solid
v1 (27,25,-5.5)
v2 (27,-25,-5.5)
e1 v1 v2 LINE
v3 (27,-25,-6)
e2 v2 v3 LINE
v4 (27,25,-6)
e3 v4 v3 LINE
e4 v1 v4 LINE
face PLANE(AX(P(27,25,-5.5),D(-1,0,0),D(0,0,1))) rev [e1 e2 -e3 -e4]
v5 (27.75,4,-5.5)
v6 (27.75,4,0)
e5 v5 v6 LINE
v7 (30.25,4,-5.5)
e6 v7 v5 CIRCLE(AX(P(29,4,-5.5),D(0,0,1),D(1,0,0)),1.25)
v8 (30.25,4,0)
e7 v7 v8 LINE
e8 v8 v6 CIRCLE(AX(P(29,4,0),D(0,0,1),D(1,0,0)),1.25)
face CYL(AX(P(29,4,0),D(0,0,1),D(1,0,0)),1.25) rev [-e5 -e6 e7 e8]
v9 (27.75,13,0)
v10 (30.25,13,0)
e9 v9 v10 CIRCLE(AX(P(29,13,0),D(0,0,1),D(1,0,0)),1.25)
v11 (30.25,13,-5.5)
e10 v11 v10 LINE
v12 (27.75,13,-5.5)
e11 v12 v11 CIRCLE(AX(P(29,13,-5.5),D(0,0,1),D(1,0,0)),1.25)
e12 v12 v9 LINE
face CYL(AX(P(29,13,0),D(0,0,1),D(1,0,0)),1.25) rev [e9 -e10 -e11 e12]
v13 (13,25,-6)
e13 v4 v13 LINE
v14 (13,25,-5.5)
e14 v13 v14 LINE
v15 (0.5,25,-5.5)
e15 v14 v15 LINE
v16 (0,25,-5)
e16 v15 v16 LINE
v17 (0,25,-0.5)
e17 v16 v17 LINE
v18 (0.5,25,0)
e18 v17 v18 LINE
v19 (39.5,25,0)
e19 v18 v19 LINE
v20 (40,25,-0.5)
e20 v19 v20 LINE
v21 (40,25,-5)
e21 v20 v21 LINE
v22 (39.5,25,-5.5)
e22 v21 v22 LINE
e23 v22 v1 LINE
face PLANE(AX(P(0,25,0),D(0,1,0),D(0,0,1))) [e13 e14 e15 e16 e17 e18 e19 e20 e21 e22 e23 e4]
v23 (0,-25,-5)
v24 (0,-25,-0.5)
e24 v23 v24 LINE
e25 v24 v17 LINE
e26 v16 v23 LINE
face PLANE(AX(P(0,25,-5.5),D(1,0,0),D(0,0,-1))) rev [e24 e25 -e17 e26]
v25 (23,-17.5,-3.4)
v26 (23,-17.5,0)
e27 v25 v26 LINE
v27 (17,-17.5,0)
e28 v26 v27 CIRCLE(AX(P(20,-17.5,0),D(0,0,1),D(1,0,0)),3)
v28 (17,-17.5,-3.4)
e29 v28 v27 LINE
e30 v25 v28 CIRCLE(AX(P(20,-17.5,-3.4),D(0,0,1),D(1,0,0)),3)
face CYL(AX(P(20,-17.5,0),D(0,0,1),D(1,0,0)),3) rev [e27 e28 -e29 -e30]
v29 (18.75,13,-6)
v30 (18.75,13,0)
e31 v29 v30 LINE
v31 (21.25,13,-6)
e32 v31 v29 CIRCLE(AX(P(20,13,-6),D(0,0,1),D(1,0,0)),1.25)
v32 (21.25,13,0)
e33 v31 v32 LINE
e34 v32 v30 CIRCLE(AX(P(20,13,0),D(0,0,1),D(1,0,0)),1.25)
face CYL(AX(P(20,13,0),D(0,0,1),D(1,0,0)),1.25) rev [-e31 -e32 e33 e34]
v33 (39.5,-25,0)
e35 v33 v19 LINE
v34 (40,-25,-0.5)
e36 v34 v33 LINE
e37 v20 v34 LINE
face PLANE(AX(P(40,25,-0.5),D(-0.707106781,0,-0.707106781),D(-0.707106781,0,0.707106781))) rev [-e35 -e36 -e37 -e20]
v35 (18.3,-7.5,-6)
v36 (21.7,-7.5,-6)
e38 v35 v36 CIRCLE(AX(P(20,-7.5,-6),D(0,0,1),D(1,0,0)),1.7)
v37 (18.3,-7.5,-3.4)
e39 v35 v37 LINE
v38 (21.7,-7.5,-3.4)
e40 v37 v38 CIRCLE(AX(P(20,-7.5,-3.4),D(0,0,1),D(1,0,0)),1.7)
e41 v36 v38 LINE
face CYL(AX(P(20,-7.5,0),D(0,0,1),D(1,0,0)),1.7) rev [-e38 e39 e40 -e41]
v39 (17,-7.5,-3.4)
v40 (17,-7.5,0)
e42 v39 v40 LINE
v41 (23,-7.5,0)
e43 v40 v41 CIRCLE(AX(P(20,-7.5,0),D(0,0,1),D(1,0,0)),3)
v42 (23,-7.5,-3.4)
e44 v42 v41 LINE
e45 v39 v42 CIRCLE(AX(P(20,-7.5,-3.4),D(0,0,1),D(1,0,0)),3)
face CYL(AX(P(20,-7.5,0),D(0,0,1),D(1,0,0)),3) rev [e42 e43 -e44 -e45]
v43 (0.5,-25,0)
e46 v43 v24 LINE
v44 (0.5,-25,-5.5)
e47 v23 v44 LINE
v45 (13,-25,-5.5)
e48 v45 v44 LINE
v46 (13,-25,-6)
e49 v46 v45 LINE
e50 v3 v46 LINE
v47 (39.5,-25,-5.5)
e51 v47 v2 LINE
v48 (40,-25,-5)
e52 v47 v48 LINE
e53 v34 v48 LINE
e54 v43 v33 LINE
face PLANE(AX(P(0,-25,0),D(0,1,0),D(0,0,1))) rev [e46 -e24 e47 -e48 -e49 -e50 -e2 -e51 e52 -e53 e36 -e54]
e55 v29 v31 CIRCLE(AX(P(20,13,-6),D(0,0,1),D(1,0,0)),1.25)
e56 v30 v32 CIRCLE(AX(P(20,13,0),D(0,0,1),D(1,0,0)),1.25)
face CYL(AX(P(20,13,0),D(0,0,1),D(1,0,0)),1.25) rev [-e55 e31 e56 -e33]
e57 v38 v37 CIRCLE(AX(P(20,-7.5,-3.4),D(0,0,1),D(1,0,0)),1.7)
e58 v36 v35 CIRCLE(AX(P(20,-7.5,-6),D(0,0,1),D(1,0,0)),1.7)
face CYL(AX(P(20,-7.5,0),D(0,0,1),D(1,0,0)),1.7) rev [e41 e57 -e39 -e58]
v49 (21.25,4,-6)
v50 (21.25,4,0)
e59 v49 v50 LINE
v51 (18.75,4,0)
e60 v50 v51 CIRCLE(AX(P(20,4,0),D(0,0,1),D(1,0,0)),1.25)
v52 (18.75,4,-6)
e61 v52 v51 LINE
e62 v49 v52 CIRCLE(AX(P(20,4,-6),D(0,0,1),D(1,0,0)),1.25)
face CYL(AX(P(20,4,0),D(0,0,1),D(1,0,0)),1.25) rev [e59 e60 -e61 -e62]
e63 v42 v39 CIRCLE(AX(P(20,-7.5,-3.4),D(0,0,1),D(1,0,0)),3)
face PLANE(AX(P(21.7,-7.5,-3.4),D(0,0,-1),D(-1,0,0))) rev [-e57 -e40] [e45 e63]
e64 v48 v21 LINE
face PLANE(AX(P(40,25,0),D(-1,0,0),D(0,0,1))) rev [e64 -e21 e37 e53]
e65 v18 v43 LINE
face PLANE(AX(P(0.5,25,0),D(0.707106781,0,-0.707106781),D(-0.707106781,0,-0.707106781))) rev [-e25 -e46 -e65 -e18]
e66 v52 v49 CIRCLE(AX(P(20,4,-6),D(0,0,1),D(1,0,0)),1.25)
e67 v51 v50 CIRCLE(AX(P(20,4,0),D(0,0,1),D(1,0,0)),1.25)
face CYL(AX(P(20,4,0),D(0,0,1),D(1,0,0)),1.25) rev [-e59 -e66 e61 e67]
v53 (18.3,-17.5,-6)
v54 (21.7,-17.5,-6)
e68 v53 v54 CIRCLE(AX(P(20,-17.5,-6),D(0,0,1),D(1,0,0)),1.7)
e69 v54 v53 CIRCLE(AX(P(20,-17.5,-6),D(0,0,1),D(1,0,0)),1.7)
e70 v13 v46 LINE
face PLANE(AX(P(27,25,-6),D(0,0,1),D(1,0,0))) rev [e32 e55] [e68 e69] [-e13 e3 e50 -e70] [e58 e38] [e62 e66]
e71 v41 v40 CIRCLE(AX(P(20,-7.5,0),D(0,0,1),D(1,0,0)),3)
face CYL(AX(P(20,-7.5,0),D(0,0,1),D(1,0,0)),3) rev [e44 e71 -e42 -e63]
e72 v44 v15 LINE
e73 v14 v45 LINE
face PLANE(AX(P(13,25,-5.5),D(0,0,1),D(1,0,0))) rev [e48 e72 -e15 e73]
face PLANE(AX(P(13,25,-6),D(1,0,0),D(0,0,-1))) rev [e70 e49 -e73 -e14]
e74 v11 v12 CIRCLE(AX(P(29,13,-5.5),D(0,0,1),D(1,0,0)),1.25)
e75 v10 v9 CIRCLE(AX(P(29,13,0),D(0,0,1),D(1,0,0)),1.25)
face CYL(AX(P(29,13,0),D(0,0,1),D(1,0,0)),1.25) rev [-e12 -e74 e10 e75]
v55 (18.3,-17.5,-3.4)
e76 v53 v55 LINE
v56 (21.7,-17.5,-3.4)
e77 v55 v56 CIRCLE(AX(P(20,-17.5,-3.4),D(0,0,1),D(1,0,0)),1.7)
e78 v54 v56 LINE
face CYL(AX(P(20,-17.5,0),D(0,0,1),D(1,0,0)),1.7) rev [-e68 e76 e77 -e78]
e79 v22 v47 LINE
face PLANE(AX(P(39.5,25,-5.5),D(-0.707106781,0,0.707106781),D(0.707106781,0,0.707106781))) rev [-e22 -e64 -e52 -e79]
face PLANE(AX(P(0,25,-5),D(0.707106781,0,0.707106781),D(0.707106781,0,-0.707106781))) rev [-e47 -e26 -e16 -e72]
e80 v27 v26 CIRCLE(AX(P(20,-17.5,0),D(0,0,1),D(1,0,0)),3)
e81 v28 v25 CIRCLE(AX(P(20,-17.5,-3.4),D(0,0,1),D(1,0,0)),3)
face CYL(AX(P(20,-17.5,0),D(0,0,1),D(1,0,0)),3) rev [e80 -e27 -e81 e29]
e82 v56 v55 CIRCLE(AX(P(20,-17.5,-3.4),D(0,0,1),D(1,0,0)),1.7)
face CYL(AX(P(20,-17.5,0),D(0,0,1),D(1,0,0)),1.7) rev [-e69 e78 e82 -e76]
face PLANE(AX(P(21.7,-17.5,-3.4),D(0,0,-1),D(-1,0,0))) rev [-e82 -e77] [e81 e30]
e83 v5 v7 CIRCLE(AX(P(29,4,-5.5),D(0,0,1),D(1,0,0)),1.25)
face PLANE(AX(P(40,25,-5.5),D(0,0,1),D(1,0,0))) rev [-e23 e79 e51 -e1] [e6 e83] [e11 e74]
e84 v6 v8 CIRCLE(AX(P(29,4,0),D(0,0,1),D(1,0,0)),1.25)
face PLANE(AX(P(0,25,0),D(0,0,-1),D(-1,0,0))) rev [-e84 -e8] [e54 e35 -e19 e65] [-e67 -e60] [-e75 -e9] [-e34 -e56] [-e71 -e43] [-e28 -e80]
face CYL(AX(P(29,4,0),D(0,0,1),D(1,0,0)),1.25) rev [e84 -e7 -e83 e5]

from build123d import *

# Parameters (mm, degrees)
BOSS_EXTRUDE1_DEPTH                                  = 25
CHAMFER1_SIZE                                        = 0.5
HOLE_SIZE_PER_SOCKET_HEAD_CAP_SCREW_TYPE_D           = 3.4
HOLE_SIZE_PER_SOCKET_HEAD_CAP_SCREW_TYPE_CBORE_D     = 6
HOLE_SIZE_PER_SOCKET_HEAD_CAP_SCREW_TYPE_CBORE_DEPTH = 3.4
M3_TAPPED_HOLE1_D                                    = 2.5
M3_TAPPED_HOLE1_DEPTH                                = 7.5
M3_TAPPED_HOLE1_TIP                                  = 0.751075774


with BuildPart() as part:
    # Sketch1 → Boss-Extrude1 (new, symmetric)
    with BuildSketch(Plane(origin=(0, 0, 0), x_dir=(1, 0, 0), z_dir=(0, 1, 0))):
        Polygon((0, 0), (40, 0), (40, 5.5), (27, 5.5), (27, 6), (13, 6), (13, 5.5), (0, 5.5), align=None)
    extrude(amount=BOSS_EXTRUDE1_DEPTH, both=True)

    # Chamfer1
    chamfer1_edges = [part.edges().sort_by_distance(p)[0] for p in [
        (0, 0, -5.5),
        (40, 0, -5.5),
        (40, 0, 0),
        (0, 0, 0),
    ]]
    chamfer(chamfer1_edges, length=CHAMFER1_SIZE)

    # Hole Size per Socket Head Cap Screw Type1 (through all)
    with Locations(Plane.XY):
        with Locations((20, -7.5), (20, -17.5)):
            CounterBoreHole(HOLE_SIZE_PER_SOCKET_HEAD_CAP_SCREW_TYPE_D / 2, HOLE_SIZE_PER_SOCKET_HEAD_CAP_SCREW_TYPE_CBORE_D / 2, HOLE_SIZE_PER_SOCKET_HEAD_CAP_SCREW_TYPE_CBORE_DEPTH)

    # M3 Tapped Hole1
    with Locations(Plane.XY):
        with Locations((20, 13), (29, 13), (20, 4), (29, 4)):
            Hole(M3_TAPPED_HOLE1_D / 2, depth=M3_TAPPED_HOLE1_DEPTH)
            with Locations((0, 0, -(M3_TAPPED_HOLE1_DEPTH + M3_TAPPED_HOLE1_TIP / 2))):  # 118° drill point
                Cone(0, M3_TAPPED_HOLE1_D / 2, M3_TAPPED_HOLE1_TIP, mode=Mode.SUBTRACT)


solid = part.part
